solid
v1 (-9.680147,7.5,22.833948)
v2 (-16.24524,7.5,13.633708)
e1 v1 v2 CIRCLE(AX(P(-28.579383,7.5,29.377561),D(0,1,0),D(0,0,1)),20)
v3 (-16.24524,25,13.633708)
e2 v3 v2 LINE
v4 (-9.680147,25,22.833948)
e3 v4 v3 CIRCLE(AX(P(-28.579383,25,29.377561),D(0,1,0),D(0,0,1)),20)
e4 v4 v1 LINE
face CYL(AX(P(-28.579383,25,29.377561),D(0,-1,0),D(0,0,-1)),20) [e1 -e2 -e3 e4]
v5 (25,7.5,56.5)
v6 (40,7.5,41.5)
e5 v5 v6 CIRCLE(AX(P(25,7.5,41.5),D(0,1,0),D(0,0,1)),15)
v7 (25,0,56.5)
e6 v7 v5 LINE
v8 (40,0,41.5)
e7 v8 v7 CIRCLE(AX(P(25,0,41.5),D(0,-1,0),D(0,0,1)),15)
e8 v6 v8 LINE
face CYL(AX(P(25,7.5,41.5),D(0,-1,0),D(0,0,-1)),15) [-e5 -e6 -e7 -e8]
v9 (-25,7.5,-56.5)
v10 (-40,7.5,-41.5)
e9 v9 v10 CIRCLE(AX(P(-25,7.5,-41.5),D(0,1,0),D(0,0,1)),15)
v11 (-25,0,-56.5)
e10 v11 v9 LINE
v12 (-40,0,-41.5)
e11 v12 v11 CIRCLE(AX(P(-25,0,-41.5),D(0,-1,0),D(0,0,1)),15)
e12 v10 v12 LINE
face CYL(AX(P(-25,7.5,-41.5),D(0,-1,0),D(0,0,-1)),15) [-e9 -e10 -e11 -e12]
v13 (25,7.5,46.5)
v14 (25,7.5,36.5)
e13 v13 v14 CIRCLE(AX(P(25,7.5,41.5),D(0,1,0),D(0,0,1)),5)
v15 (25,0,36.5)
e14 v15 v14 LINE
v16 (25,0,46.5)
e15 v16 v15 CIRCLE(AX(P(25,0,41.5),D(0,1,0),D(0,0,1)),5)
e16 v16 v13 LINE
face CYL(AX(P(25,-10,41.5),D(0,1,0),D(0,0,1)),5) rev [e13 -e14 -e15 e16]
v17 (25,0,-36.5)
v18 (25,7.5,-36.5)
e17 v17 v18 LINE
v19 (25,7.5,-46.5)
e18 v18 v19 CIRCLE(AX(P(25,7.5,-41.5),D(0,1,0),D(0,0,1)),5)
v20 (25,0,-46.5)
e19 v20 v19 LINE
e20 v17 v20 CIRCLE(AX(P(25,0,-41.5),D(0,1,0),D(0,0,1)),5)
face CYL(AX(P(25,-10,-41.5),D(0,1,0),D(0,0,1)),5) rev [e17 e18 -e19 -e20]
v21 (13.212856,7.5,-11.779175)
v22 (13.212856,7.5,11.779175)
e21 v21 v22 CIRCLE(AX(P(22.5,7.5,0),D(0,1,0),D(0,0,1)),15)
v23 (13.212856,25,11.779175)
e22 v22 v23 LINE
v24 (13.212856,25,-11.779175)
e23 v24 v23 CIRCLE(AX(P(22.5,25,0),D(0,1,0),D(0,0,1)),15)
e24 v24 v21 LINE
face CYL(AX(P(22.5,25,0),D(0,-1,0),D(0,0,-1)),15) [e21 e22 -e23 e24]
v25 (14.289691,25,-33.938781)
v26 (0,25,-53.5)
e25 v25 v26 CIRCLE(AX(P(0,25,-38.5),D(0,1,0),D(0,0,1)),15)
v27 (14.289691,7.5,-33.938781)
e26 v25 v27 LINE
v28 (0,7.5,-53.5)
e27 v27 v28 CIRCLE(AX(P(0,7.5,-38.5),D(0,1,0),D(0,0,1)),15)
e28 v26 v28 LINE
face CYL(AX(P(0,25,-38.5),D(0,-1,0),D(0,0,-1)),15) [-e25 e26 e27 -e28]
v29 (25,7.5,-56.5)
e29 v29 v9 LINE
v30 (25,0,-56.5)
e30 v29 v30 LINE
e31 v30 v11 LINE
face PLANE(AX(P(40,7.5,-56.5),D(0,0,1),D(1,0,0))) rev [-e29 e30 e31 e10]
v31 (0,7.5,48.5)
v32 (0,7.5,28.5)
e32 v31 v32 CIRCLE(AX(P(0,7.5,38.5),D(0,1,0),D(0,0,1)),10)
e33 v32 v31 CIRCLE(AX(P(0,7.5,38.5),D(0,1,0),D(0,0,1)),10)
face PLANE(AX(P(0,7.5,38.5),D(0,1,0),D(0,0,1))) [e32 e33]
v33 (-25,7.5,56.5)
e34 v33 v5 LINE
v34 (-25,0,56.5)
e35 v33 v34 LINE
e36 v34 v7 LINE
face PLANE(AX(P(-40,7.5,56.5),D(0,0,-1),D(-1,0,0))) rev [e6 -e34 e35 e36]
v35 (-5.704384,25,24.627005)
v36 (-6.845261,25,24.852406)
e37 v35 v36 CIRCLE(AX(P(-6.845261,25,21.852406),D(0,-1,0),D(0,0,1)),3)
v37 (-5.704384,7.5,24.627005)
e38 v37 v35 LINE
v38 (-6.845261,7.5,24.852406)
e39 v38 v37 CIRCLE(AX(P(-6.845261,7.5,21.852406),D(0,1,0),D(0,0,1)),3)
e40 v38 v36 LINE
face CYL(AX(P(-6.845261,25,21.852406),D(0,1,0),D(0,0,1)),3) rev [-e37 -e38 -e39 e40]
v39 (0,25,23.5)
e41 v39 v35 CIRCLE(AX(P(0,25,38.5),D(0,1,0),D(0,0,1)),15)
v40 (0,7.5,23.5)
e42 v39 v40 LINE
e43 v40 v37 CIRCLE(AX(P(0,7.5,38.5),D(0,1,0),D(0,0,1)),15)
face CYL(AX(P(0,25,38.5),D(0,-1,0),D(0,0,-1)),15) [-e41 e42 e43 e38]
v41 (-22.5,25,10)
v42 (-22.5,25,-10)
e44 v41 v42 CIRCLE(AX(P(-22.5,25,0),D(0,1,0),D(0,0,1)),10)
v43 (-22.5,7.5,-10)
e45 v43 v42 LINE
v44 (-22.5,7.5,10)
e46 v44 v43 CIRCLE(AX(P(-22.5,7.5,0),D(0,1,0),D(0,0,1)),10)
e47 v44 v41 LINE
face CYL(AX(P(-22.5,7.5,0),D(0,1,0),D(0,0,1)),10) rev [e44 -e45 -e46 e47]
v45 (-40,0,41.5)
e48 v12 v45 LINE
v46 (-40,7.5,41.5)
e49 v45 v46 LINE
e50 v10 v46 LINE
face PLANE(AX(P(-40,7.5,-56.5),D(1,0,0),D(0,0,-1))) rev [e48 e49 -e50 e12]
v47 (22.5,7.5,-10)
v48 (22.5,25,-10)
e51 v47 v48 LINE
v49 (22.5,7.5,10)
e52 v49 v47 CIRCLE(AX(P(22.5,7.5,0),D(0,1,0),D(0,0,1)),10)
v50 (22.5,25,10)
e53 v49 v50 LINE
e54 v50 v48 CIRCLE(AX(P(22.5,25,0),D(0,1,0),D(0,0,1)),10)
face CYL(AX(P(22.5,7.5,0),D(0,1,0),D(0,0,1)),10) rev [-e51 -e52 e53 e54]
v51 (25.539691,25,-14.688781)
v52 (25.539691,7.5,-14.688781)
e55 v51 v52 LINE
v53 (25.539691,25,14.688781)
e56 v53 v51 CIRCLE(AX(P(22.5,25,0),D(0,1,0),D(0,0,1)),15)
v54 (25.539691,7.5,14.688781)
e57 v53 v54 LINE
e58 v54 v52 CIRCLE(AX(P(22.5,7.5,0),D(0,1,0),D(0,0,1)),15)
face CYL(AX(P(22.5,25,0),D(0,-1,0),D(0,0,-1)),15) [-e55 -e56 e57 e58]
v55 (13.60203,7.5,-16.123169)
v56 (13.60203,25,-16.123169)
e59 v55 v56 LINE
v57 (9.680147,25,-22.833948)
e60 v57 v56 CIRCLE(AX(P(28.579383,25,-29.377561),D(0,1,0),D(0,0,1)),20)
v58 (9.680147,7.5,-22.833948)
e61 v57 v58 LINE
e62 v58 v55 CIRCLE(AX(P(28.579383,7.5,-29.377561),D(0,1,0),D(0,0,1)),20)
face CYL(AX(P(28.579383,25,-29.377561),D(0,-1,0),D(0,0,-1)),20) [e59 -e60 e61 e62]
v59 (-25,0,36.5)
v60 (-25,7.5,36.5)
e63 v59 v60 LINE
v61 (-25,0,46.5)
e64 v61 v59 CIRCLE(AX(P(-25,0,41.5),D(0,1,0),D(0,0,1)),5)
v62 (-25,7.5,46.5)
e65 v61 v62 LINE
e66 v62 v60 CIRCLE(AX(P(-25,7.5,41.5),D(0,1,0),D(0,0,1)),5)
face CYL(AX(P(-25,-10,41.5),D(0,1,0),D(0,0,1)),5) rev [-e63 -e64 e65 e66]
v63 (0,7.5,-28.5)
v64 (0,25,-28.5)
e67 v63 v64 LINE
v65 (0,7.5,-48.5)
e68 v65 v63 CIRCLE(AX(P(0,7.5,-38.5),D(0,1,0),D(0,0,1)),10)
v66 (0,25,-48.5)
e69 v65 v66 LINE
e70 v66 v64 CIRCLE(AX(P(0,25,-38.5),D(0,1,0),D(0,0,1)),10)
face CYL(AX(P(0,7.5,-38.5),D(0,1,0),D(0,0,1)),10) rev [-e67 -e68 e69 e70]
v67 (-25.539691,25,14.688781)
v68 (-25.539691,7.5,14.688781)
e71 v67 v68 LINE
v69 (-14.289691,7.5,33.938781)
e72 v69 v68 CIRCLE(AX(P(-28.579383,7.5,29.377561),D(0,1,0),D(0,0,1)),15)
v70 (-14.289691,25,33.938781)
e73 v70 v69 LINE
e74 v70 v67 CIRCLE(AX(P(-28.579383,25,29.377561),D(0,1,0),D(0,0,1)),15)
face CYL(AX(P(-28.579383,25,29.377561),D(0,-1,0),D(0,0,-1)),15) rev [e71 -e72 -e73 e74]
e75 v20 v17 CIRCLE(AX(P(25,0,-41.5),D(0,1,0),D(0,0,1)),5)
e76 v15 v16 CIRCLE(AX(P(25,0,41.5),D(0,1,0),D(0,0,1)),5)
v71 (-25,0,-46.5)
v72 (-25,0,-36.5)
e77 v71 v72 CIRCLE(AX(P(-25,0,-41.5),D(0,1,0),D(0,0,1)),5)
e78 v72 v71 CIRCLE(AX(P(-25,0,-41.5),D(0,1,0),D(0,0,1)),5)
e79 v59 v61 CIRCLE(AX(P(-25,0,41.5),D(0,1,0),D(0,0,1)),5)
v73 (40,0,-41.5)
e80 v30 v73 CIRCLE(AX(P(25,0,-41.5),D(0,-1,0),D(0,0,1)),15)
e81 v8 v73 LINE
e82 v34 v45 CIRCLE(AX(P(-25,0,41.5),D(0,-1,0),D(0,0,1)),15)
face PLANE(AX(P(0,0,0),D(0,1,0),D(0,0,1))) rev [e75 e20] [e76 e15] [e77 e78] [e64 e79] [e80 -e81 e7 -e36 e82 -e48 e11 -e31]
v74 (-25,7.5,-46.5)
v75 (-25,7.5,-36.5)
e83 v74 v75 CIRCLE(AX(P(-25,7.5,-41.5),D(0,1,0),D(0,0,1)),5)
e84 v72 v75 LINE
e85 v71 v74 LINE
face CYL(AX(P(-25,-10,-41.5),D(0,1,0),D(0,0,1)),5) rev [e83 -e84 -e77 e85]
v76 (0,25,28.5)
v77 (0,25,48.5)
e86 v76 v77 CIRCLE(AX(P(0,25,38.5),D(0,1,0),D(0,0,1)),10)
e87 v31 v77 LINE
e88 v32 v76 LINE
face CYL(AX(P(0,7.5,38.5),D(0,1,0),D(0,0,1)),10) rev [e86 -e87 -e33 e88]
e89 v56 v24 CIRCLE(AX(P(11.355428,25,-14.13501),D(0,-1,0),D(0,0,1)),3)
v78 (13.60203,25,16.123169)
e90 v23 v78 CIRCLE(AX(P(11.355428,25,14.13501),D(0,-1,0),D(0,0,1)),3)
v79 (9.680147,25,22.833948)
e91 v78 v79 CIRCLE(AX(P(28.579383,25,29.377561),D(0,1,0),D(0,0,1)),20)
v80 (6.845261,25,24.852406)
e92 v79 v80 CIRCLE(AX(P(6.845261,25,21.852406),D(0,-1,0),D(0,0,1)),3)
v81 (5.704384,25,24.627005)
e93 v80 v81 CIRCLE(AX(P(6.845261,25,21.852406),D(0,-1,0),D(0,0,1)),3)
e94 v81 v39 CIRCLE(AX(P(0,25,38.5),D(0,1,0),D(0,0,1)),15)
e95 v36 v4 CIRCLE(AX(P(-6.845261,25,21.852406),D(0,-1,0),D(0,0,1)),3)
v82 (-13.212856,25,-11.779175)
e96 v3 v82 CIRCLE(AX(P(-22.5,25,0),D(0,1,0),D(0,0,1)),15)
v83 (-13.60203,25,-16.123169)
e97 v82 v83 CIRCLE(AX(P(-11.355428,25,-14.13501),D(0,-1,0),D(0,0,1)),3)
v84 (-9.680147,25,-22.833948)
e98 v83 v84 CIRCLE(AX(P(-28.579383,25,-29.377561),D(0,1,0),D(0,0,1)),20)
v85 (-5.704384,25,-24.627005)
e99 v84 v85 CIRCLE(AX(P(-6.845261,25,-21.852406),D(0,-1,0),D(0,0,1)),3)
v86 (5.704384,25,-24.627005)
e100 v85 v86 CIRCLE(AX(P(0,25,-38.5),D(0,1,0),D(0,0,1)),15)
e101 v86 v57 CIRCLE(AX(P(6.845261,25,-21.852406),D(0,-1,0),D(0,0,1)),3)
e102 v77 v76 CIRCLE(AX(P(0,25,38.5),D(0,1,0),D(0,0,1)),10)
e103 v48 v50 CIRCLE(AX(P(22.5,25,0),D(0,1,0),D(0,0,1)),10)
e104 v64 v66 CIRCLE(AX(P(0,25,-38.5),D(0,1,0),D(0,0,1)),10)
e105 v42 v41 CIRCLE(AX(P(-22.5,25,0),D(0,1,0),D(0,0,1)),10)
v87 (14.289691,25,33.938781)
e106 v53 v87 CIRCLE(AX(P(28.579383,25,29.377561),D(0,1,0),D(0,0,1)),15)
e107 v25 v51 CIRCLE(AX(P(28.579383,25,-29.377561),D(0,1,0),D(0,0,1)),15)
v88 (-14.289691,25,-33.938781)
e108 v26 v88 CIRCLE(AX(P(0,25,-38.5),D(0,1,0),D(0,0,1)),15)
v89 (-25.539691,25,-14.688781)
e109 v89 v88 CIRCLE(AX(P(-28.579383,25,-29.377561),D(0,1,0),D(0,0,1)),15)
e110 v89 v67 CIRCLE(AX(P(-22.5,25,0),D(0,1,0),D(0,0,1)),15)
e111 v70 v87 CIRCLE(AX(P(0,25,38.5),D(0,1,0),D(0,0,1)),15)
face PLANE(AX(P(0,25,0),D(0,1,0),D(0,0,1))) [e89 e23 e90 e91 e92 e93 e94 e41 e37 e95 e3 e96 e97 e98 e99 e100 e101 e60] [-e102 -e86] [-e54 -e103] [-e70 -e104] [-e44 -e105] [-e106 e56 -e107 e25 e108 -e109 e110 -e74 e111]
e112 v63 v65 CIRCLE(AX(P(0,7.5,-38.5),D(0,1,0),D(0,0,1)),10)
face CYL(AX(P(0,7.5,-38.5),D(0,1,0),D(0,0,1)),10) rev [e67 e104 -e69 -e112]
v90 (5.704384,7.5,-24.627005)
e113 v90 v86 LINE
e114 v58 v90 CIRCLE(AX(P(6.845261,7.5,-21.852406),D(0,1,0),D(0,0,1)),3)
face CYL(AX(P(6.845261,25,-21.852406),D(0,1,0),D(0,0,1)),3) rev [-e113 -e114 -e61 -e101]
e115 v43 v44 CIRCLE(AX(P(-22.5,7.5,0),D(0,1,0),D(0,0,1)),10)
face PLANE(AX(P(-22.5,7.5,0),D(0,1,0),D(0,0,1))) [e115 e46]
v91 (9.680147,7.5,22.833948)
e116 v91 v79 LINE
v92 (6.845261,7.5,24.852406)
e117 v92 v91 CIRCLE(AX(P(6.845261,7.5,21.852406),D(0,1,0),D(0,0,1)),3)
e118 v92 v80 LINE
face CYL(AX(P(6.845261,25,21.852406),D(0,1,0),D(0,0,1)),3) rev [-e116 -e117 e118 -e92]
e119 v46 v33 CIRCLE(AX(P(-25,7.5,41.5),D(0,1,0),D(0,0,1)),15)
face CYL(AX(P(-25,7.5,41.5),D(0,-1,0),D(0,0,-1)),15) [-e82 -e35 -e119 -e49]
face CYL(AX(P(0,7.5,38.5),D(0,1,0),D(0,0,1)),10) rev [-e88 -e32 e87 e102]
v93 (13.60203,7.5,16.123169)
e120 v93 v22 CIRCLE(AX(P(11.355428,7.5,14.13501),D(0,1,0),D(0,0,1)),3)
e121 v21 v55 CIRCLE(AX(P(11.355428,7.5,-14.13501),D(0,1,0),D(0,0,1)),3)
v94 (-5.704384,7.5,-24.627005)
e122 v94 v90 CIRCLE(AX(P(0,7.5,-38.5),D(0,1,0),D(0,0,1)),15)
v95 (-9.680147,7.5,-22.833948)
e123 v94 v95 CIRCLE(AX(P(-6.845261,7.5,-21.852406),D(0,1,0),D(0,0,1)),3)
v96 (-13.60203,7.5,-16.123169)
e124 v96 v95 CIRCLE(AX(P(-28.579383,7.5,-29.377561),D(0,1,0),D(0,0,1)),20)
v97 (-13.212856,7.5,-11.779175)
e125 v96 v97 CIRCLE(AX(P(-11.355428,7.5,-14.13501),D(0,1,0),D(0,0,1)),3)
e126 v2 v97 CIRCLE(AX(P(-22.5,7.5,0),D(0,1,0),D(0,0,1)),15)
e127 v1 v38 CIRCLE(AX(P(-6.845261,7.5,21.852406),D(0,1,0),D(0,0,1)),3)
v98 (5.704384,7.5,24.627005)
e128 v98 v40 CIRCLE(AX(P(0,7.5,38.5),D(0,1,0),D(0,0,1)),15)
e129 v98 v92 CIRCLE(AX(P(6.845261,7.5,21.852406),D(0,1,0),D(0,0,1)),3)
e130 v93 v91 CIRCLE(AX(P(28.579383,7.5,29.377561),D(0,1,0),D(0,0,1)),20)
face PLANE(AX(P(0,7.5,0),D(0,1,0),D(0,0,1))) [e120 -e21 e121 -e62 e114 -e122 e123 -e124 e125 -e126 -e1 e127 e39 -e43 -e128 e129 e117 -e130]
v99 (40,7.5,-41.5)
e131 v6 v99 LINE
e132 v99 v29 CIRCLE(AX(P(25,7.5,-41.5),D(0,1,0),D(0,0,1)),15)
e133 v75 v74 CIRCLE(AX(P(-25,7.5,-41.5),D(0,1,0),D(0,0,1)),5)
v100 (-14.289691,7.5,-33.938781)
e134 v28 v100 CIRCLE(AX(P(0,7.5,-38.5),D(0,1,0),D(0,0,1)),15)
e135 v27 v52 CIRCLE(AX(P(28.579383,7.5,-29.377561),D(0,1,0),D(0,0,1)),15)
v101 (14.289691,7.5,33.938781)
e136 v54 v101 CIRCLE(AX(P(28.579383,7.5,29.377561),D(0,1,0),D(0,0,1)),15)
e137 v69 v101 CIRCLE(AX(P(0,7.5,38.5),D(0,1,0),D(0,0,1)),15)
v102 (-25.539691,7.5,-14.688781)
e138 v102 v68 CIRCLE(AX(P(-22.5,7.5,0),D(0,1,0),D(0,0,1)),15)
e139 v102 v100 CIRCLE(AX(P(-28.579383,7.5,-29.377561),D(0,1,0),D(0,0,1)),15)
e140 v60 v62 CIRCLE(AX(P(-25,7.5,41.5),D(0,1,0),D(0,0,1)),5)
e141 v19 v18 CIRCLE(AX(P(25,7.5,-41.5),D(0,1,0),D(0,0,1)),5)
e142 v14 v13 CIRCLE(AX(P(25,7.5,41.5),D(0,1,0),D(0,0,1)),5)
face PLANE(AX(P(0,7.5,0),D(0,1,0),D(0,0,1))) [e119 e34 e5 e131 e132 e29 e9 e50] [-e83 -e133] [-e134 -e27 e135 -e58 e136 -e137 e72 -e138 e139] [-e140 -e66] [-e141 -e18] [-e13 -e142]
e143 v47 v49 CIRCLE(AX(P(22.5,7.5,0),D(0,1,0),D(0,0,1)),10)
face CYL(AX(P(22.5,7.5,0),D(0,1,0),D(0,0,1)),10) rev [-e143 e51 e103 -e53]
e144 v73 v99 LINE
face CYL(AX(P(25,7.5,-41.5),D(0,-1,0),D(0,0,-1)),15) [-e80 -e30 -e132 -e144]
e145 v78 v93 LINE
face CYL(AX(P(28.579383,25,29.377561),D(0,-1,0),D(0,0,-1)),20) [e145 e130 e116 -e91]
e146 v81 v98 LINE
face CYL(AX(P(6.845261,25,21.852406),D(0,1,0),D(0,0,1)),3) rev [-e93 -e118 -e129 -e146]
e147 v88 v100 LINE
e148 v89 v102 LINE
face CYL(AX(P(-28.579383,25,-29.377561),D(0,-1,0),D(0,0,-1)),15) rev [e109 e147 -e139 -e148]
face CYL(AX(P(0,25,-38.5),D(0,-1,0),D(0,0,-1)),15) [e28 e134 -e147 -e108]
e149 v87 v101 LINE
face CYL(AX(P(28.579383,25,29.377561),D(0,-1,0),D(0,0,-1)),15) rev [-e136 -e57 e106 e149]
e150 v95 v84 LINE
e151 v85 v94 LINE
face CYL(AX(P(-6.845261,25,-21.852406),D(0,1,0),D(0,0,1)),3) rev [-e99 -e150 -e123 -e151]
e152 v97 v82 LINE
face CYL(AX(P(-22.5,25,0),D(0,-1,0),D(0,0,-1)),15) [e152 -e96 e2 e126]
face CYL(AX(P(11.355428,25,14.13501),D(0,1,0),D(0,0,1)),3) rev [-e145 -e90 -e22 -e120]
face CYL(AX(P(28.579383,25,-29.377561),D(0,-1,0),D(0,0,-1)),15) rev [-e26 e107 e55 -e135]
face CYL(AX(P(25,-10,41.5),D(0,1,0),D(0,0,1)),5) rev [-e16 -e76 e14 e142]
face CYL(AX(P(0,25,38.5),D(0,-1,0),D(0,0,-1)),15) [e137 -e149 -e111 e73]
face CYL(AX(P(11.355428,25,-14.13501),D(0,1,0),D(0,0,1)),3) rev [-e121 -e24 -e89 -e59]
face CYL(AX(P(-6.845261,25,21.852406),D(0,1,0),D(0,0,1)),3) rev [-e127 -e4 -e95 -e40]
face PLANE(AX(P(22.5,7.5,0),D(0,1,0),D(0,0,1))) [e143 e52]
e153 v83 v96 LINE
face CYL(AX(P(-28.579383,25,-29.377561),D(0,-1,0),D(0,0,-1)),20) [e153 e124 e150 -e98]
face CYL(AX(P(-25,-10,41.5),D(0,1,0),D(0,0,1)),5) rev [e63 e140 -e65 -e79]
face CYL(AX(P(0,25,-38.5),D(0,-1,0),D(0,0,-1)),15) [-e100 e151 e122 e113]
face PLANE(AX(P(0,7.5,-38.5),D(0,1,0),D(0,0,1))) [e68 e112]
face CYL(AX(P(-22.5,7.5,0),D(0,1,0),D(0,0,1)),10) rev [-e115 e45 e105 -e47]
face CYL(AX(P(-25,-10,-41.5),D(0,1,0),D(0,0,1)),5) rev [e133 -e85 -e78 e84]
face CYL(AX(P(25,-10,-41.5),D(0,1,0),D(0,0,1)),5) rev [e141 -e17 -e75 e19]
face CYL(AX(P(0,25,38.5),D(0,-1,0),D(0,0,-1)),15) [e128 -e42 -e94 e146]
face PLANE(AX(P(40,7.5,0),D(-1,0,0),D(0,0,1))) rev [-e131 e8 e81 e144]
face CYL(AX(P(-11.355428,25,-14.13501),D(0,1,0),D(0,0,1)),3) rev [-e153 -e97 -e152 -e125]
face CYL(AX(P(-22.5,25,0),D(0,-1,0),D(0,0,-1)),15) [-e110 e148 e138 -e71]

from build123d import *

# Parameters (mm, degrees)
BASE_PLATE_DEPTH            = 7.5
PORT_BOSS_SKETCH_R          = 15
QUAD_PORT_BOSS_DEPTH        = 17.5
BOSS_FILLET_R3_A_R          = 3
BOSS_FILLET_R3_B_R          = 3
BOSS_FILLET_R3_C_R          = 3
BOSS_FILLET_R3_D_R          = 3
BOSS_FILLET_R3_E_R          = 3
BOSS_FILLET_R3_F_R          = 3
BOSS_FILLET_R3_G_R          = 3
CENTRAL_CAVITY_SKETCH_R     = 10
CENTRAL_CAVITY_DEPTH        = 17.5
PLATE_CORNER_FILLET_R15_A_R = 15
PLATE_CORNER_FILLET_R15_B_R = 15
PLATE_CORNER_FILLET_R15_C_R = 15
PLATE_CORNER_FILLET_R15_D_R = 15
MOUNTING_HOLES_SKETCH_R     = 5
MOUNTING_HOLES_4X_DEPTH     = 17.5


with BuildPart() as part:
    # Base Plate Sketch → Base Plate (new body)
    with BuildSketch(Plane(origin=(0, 0, 0), x_dir=(1, 0, 0), z_dir=(0, 1, 0))):
        Polygon((40, 0), (40, 56.5), (-40, 56.5), (-40, -56.5), (40, -56.5), align=None)
    extrude(amount=BASE_PLATE_DEPTH)

    # Port Boss Sketch → Quad Port Boss (add)
    with BuildSketch(Plane(origin=(0, 7.5, 0), x_dir=(1, 0, 0), z_dir=(0, 1, 0))):
        with BuildLine():
            ThreePointArc((8.808525392, 26.35875293), (11.311943753, 19.286200894), (16.245240248, 13.633707509))
            ThreePointArc((16.245240248, 13.633707509), (20.808119068, 14.904279215), (25.539691318, 14.68878064))
            ThreePointArc((25.539691318, 14.68878064), (15.628803473, 21.809040991), (14.289691318, 33.93878064))
            ThreePointArc((14.289691318, 33.93878064), (12.155085718, 29.710580725), (8.808525392, 26.35875293))
        make_face()
        with Locations((22.5, 0)):
            Circle(PORT_BOSS_SKETCH_R)
        with BuildLine():
            ThreePointArc((8.808525392, -26.35875293), (12.155085718, -29.710580725), (14.289691318, -33.93878064))
            ThreePointArc((14.289691318, -33.93878064), (15.628803473, -21.809040991), (25.539691318, -14.68878064))
            ThreePointArc((25.539691318, -14.68878064), (20.808119068, -14.904279215), (16.245240248, -13.633707509))
            ThreePointArc((16.245240248, -13.633707509), (11.311943753, -19.286200894), (8.808525392, -26.35875293))
        make_face()
        with Locations((0, -38.5)):
            Circle(PORT_BOSS_SKETCH_R)
        with BuildLine():
            ThreePointArc((-25.539691318, -14.68878064), (-15.628803473, -21.809040991), (-14.289691318, -33.93878064))
            ThreePointArc((-14.289691318, -33.93878064), (-12.155085718, -29.710580725), (-8.808525392, -26.35875293))
            ThreePointArc((-8.808525392, -26.35875293), (-11.311943753, -19.286200894), (-16.245240248, -13.633707509))
            ThreePointArc((-16.245240248, -13.633707509), (-20.808119068, -14.904279215), (-25.539691318, -14.68878064))
        make_face()
        with Locations((-22.5, 0)):
            Circle(PORT_BOSS_SKETCH_R)
        with BuildLine():
            ThreePointArc((-14.289691318, 33.93878064), (-15.628803473, 21.809040991), (-25.539691318, 14.68878064))
            ThreePointArc((-25.539691318, 14.68878064), (-20.808119068, 14.904279215), (-16.245240248, 13.633707509))
            ThreePointArc((-16.245240248, 13.633707509), (-11.311943753, 19.286200894), (-8.808525392, 26.35875293))
            ThreePointArc((-8.808525392, 26.35875293), (-12.155085718, 29.710580725), (-14.289691318, 33.93878064))
        make_face()
        with Locations((0, 38.5)):
            Circle(PORT_BOSS_SKETCH_R)
    extrude(amount=QUAD_PORT_BOSS_DEPTH)

    # Boss Fillet R3 A
    boss_fillet_r3_a_edges = [part.edges().sort_by_distance(p)[0] for p in [
        (-8.808525392, 16.25, -26.35875293),
    ]]
    fillet(boss_fillet_r3_a_edges, radius=BOSS_FILLET_R3_A_R)

    # Boss Fillet R3 B
    boss_fillet_r3_b_edges = [part.edges().sort_by_distance(p)[0] for p in [
        (8.808525392, 16.25, -26.35875293),
    ]]
    fillet(boss_fillet_r3_b_edges, radius=BOSS_FILLET_R3_B_R)

    # Boss Fillet R3 C
    boss_fillet_r3_c_edges = [part.edges().sort_by_distance(p)[0] for p in [
        (16.245240248, 16.25, -13.633707509),
    ]]
    fillet(boss_fillet_r3_c_edges, radius=BOSS_FILLET_R3_C_R)

    # Boss Fillet R3 D
    boss_fillet_r3_d_edges = [part.edges().sort_by_distance(p)[0] for p in [
        (16.245240248, 16.25, 13.633707509),
    ]]
    fillet(boss_fillet_r3_d_edges, radius=BOSS_FILLET_R3_D_R)

    # Boss Fillet R3 E
    boss_fillet_r3_e_edges = [part.edges().sort_by_distance(p)[0] for p in [
        (-16.245240248, 16.25, -13.633707509),
    ]]
    fillet(boss_fillet_r3_e_edges, radius=BOSS_FILLET_R3_E_R)

    # Boss Fillet R3 F
    boss_fillet_r3_f_edges = [part.edges().sort_by_distance(p)[0] for p in [
        (-8.808525392, 16.25, 26.35875293),
    ]]
    fillet(boss_fillet_r3_f_edges, radius=BOSS_FILLET_R3_F_R)

    # Boss Fillet R3 G
    boss_fillet_r3_g_edges = [part.edges().sort_by_distance(p)[0] for p in [
        (8.808525392, 16.25, 26.35875293),
    ]]
    fillet(boss_fillet_r3_g_edges, radius=BOSS_FILLET_R3_G_R)

    # Central Cavity Sketch → Central Cavity (cut)
    with BuildSketch(Plane(origin=(0, 25, 0), x_dir=(1, 0, 0), z_dir=(0, 1, 0))):
        with Locations(Location((0, 38.5, 0), (0, 0, 270))):
            Circle(CENTRAL_CAVITY_SKETCH_R)
        with Locations(Location((22.5, 0, 0), (0, 0, 270))):
            Circle(CENTRAL_CAVITY_SKETCH_R)
        with Locations(Location((0, -38.5, 0), (0, 0, 270))):
            Circle(CENTRAL_CAVITY_SKETCH_R)
        with Locations(Location((-22.5, 0, 0), (0, 0, 270))):
            Circle(CENTRAL_CAVITY_SKETCH_R)
    extrude(amount=-CENTRAL_CAVITY_DEPTH, mode=Mode.SUBTRACT)

    # Plate Corner Fillet R15 A
    plate_corner_fillet_r15_a_edges = [part.edges().sort_by_distance(p)[0] for p in [
        (-40, 3.75, -56.5),
    ]]
    fillet(plate_corner_fillet_r15_a_edges, radius=PLATE_CORNER_FILLET_R15_A_R)

    # Plate Corner Fillet R15 B
    plate_corner_fillet_r15_b_edges = [part.edges().sort_by_distance(p)[0] for p in [
        (40, 3.75, -56.5),
    ]]
    fillet(plate_corner_fillet_r15_b_edges, radius=PLATE_CORNER_FILLET_R15_B_R)

    # Plate Corner Fillet R15 C
    plate_corner_fillet_r15_c_edges = [part.edges().sort_by_distance(p)[0] for p in [
        (40, 3.75, 56.5),
    ]]
    fillet(plate_corner_fillet_r15_c_edges, radius=PLATE_CORNER_FILLET_R15_C_R)

    # Plate Corner Fillet R15 D
    plate_corner_fillet_r15_d_edges = [part.edges().sort_by_distance(p)[0] for p in [
        (-40, 3.75, 56.5),
    ]]
    fillet(plate_corner_fillet_r15_d_edges, radius=PLATE_CORNER_FILLET_R15_D_R)

    # Mounting Holes Sketch → Mounting Holes 4x (cut)
    with BuildSketch(Plane(origin=(0, 7.5, 0), x_dir=(1, 0, 0), z_dir=(0, 1, 0))):
        with Locations(Location((-25, 41.5, 0), (0, 0, 270))):
            Circle(MOUNTING_HOLES_SKETCH_R)
        with Locations(Location((25, 41.5, 0), (0, 0, 270))):
            Circle(MOUNTING_HOLES_SKETCH_R)
        with Locations(Location((25, -41.5, 0), (0, 0, 270))):
            Circle(MOUNTING_HOLES_SKETCH_R)
        with Locations(Location((-25, -41.5, 0), (0, 0, 270))):
            Circle(MOUNTING_HOLES_SKETCH_R)
    extrude(amount=-MOUNTING_HOLES_4X_DEPTH, mode=Mode.SUBTRACT)


solid = part.part
